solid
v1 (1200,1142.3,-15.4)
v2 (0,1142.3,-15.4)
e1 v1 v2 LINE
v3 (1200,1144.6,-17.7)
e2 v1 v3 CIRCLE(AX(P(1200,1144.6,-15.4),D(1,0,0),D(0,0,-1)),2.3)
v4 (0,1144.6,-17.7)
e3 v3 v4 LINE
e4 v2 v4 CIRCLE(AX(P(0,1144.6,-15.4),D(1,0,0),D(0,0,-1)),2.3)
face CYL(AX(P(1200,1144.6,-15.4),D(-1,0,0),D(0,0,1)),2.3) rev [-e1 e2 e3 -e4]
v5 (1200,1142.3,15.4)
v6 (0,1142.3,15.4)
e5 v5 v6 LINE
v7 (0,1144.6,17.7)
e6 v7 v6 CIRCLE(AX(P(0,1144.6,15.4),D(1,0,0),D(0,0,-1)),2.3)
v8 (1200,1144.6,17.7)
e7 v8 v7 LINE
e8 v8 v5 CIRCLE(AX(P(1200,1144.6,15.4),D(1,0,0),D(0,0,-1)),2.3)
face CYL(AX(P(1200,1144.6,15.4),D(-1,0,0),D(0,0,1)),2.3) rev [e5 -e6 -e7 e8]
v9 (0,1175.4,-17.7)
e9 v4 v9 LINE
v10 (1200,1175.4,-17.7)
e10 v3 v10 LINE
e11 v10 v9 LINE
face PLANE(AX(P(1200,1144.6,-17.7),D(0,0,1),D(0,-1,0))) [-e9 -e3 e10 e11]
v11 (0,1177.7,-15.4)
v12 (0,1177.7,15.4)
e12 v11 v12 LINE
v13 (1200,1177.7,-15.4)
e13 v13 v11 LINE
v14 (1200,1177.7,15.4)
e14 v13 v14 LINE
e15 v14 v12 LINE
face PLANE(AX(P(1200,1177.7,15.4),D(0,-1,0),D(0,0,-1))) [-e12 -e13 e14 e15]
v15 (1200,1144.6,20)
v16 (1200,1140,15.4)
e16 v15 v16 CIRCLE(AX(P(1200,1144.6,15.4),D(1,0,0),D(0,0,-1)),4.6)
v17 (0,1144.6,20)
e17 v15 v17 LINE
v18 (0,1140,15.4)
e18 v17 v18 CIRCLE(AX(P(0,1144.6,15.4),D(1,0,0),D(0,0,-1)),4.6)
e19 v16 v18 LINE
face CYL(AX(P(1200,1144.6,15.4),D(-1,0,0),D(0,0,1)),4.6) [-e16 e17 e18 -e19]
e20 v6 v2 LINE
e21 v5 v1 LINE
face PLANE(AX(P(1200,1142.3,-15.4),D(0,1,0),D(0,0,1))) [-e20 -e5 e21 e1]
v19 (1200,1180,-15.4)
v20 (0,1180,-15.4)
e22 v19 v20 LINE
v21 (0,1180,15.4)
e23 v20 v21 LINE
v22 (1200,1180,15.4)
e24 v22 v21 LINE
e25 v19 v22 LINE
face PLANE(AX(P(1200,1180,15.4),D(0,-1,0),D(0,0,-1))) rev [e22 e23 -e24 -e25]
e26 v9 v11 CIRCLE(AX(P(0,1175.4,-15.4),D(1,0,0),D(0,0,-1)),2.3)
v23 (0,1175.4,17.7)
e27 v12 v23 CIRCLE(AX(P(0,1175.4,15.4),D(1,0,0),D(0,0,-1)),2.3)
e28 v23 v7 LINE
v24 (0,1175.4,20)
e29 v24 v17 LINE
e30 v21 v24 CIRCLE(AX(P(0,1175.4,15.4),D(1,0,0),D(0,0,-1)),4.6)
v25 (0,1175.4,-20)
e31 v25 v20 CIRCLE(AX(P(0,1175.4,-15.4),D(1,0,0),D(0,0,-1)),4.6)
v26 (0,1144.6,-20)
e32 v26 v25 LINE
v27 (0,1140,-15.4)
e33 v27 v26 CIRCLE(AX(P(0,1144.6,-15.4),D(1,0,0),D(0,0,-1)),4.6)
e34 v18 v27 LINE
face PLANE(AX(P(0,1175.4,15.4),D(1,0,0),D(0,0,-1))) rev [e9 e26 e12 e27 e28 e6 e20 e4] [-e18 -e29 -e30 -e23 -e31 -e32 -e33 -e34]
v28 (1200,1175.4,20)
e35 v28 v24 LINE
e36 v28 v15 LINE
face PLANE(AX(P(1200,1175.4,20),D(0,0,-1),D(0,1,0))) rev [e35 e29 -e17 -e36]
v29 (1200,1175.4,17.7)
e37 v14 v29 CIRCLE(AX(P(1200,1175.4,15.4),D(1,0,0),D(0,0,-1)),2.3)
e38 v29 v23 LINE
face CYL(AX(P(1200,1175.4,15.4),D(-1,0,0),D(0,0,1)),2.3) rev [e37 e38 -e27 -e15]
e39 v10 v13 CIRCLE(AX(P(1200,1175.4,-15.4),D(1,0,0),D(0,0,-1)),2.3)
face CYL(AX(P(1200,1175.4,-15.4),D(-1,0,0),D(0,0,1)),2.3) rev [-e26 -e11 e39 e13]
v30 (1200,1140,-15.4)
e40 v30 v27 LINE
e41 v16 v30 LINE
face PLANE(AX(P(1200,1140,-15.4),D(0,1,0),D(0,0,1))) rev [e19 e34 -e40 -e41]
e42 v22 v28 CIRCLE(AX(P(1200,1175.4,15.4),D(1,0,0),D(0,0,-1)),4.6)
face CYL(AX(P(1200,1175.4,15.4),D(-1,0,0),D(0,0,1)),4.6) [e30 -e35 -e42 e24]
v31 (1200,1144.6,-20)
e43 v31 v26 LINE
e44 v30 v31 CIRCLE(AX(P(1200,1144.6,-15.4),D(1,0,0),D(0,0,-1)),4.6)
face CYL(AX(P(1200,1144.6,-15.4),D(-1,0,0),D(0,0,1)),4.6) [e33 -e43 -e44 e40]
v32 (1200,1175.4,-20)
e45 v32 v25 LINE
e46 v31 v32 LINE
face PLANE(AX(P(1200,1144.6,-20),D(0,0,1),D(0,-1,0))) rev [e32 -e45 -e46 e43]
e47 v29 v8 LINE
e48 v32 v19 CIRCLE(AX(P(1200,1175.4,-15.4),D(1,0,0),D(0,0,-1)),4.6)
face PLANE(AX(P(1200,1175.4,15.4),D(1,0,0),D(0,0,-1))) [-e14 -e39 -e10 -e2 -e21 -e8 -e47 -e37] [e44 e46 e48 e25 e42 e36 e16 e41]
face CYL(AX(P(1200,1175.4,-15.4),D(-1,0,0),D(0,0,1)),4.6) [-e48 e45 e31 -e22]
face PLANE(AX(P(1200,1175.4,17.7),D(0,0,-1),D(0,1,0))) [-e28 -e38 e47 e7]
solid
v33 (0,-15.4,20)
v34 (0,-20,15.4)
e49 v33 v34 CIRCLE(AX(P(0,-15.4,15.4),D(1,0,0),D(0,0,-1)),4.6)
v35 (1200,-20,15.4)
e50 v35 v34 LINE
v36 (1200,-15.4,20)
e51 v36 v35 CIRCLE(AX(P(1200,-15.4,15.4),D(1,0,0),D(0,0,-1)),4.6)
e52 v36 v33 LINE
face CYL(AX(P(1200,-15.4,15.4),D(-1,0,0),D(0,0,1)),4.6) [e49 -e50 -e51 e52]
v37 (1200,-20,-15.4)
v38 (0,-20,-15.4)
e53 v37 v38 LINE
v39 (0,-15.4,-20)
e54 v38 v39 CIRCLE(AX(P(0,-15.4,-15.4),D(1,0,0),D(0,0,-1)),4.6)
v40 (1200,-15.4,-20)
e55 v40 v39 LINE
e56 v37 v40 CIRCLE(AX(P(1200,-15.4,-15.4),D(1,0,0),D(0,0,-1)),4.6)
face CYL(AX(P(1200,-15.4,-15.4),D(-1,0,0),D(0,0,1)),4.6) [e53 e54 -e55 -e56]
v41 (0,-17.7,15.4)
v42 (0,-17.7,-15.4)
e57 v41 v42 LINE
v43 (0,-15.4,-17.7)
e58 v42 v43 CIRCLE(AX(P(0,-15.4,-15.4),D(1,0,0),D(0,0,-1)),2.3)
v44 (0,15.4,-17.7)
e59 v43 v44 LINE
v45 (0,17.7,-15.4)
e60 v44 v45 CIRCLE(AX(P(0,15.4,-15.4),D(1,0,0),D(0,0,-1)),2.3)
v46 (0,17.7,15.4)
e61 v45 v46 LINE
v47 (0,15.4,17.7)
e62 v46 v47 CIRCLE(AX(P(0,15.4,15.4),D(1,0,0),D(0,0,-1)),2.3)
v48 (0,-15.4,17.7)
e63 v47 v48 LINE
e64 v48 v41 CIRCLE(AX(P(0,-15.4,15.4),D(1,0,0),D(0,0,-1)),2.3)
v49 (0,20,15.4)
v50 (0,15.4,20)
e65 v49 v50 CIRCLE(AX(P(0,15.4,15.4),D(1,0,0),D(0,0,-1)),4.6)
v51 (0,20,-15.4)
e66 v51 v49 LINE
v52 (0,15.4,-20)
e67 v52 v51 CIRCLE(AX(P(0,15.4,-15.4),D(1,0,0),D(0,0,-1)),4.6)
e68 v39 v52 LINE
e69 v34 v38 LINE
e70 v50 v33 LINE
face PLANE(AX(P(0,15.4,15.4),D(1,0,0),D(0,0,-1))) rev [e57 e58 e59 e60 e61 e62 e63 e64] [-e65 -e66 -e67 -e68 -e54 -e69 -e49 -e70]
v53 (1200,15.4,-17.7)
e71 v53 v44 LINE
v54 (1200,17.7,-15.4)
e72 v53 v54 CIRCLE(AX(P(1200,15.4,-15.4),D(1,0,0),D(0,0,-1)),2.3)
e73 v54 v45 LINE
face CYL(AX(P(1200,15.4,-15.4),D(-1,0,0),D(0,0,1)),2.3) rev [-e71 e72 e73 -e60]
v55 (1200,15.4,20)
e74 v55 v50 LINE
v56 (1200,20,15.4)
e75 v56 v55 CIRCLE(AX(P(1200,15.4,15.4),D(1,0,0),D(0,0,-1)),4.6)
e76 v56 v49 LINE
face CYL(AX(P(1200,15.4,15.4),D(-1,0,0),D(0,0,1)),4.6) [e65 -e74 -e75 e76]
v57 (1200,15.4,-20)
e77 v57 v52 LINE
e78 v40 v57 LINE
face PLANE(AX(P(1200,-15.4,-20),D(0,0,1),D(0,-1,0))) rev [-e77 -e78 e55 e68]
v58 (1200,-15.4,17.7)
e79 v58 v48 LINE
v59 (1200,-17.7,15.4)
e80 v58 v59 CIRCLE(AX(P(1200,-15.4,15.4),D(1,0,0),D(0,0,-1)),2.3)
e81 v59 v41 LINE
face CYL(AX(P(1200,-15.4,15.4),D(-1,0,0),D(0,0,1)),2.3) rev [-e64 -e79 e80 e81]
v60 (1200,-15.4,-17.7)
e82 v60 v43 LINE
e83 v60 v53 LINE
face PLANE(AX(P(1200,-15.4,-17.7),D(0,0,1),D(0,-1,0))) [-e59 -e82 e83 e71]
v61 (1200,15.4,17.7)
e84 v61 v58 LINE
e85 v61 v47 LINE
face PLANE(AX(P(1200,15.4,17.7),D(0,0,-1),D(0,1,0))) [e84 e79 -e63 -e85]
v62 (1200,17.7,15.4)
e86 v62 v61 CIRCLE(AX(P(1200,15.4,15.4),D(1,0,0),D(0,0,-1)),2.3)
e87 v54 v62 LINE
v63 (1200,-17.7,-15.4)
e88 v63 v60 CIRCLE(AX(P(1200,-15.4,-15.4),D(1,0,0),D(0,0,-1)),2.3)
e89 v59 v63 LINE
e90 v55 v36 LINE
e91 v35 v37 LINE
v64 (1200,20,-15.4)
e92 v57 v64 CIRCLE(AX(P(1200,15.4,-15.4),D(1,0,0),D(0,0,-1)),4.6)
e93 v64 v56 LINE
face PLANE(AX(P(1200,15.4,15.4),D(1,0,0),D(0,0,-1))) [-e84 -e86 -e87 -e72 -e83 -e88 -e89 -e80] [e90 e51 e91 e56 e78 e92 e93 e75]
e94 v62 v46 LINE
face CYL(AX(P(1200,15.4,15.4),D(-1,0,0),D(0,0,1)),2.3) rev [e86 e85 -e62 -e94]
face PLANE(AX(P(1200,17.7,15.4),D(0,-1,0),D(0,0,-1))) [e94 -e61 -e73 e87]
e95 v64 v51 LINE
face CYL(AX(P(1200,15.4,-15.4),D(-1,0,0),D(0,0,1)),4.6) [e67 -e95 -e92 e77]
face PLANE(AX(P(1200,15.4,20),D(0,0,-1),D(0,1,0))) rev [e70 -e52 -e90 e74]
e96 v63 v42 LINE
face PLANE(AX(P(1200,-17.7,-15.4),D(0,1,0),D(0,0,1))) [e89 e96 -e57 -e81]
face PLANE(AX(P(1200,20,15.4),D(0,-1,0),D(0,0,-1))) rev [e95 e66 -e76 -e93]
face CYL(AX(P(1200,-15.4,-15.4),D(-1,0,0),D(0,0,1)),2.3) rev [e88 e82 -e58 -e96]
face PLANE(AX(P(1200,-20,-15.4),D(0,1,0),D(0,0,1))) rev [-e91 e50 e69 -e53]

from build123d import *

# Parameters (mm, degrees)
SQUARE_TUBE_40_X_40_X_2_3_1_DEPTH   = 1200
SQUARE_TUBE_40_X_40_X_2_3_1_2_DEPTH = 1200


with BuildPart() as part:
    # Sketch11 → Square Tube 40 X 40 X 2.3(1) (new body)
    with BuildSketch(Plane.YZ):
        with BuildLine():
            Line((-15.4, -20), (15.4, -20))
            ThreePointArc((15.4, -20), (18.652691193, -18.652691193), (20, -15.4))
            Line((20, -15.4), (20, 15.4))
            ThreePointArc((20, 15.4), (18.652691193, 18.652691193), (15.4, 20))
            Line((15.4, 20), (-15.4, 20))
            ThreePointArc((-15.4, 20), (-18.652691193, 18.652691193), (-20, 15.4))
            Line((-20, 15.4), (-20, -15.4))
            ThreePointArc((-20, -15.4), (-18.652691193, -18.652691193), (-15.4, -20))
        make_face()
        with BuildLine():
            Line((-15.4, -17.7), (15.4, -17.7))
            ThreePointArc((15.4, -17.7), (17.026345597, -17.026345597), (17.7, -15.4))
            Line((17.7, -15.4), (17.7, 15.4))
            ThreePointArc((17.7, 15.4), (17.026345597, 17.026345597), (15.4, 17.7))
            Line((15.4, 17.7), (-15.4, 17.7))
            ThreePointArc((-15.4, 17.7), (-17.026345597, 17.026345597), (-17.7, 15.4))
            Line((-17.7, 15.4), (-17.7, -15.4))
            ThreePointArc((-17.7, -15.4), (-17.026345597, -17.026345597), (-15.4, -17.7))
        make_face(mode=Mode.SUBTRACT)
    extrude(amount=SQUARE_TUBE_40_X_40_X_2_3_1_DEPTH)


with BuildPart() as body_2:
    # Sketch11 on segment 2 (carried to segment 2) → Square Tube 40 X 40 X 2.3_1 2 (new body)
    with BuildSketch(Plane(origin=(0, 1160, 0), x_dir=(0, 1, 0), z_dir=(1, 0, 0))):
        with BuildLine():
            Line((-15.4, -20), (15.4, -20))
            ThreePointArc((15.4, -20), (18.652691193, -18.652691193), (20, -15.4))
            Line((20, -15.4), (20, 15.4))
            ThreePointArc((20, 15.4), (18.652691193, 18.652691193), (15.4, 20))
            Line((15.4, 20), (-15.4, 20))
            ThreePointArc((-15.4, 20), (-18.652691193, 18.652691193), (-20, 15.4))
            Line((-20, 15.4), (-20, -15.4))
            ThreePointArc((-20, -15.4), (-18.652691193, -18.652691193), (-15.4, -20))
        make_face()
        with BuildLine():
            Line((-15.4, -17.7), (15.4, -17.7))
            ThreePointArc((15.4, -17.7), (17.026345597, -17.026345597), (17.7, -15.4))
            Line((17.7, -15.4), (17.7, 15.4))
            ThreePointArc((17.7, 15.4), (17.026345597, 17.026345597), (15.4, 17.7))
            Line((15.4, 17.7), (-15.4, 17.7))
            ThreePointArc((-15.4, 17.7), (-17.026345597, 17.026345597), (-17.7, 15.4))
            Line((-17.7, 15.4), (-17.7, -15.4))
            ThreePointArc((-17.7, -15.4), (-17.026345597, -17.026345597), (-15.4, -17.7))
        make_face(mode=Mode.SUBTRACT)
    extrude(amount=SQUARE_TUBE_40_X_40_X_2_3_1_2_DEPTH)


solid = Compound([part.part, body_2.part])
